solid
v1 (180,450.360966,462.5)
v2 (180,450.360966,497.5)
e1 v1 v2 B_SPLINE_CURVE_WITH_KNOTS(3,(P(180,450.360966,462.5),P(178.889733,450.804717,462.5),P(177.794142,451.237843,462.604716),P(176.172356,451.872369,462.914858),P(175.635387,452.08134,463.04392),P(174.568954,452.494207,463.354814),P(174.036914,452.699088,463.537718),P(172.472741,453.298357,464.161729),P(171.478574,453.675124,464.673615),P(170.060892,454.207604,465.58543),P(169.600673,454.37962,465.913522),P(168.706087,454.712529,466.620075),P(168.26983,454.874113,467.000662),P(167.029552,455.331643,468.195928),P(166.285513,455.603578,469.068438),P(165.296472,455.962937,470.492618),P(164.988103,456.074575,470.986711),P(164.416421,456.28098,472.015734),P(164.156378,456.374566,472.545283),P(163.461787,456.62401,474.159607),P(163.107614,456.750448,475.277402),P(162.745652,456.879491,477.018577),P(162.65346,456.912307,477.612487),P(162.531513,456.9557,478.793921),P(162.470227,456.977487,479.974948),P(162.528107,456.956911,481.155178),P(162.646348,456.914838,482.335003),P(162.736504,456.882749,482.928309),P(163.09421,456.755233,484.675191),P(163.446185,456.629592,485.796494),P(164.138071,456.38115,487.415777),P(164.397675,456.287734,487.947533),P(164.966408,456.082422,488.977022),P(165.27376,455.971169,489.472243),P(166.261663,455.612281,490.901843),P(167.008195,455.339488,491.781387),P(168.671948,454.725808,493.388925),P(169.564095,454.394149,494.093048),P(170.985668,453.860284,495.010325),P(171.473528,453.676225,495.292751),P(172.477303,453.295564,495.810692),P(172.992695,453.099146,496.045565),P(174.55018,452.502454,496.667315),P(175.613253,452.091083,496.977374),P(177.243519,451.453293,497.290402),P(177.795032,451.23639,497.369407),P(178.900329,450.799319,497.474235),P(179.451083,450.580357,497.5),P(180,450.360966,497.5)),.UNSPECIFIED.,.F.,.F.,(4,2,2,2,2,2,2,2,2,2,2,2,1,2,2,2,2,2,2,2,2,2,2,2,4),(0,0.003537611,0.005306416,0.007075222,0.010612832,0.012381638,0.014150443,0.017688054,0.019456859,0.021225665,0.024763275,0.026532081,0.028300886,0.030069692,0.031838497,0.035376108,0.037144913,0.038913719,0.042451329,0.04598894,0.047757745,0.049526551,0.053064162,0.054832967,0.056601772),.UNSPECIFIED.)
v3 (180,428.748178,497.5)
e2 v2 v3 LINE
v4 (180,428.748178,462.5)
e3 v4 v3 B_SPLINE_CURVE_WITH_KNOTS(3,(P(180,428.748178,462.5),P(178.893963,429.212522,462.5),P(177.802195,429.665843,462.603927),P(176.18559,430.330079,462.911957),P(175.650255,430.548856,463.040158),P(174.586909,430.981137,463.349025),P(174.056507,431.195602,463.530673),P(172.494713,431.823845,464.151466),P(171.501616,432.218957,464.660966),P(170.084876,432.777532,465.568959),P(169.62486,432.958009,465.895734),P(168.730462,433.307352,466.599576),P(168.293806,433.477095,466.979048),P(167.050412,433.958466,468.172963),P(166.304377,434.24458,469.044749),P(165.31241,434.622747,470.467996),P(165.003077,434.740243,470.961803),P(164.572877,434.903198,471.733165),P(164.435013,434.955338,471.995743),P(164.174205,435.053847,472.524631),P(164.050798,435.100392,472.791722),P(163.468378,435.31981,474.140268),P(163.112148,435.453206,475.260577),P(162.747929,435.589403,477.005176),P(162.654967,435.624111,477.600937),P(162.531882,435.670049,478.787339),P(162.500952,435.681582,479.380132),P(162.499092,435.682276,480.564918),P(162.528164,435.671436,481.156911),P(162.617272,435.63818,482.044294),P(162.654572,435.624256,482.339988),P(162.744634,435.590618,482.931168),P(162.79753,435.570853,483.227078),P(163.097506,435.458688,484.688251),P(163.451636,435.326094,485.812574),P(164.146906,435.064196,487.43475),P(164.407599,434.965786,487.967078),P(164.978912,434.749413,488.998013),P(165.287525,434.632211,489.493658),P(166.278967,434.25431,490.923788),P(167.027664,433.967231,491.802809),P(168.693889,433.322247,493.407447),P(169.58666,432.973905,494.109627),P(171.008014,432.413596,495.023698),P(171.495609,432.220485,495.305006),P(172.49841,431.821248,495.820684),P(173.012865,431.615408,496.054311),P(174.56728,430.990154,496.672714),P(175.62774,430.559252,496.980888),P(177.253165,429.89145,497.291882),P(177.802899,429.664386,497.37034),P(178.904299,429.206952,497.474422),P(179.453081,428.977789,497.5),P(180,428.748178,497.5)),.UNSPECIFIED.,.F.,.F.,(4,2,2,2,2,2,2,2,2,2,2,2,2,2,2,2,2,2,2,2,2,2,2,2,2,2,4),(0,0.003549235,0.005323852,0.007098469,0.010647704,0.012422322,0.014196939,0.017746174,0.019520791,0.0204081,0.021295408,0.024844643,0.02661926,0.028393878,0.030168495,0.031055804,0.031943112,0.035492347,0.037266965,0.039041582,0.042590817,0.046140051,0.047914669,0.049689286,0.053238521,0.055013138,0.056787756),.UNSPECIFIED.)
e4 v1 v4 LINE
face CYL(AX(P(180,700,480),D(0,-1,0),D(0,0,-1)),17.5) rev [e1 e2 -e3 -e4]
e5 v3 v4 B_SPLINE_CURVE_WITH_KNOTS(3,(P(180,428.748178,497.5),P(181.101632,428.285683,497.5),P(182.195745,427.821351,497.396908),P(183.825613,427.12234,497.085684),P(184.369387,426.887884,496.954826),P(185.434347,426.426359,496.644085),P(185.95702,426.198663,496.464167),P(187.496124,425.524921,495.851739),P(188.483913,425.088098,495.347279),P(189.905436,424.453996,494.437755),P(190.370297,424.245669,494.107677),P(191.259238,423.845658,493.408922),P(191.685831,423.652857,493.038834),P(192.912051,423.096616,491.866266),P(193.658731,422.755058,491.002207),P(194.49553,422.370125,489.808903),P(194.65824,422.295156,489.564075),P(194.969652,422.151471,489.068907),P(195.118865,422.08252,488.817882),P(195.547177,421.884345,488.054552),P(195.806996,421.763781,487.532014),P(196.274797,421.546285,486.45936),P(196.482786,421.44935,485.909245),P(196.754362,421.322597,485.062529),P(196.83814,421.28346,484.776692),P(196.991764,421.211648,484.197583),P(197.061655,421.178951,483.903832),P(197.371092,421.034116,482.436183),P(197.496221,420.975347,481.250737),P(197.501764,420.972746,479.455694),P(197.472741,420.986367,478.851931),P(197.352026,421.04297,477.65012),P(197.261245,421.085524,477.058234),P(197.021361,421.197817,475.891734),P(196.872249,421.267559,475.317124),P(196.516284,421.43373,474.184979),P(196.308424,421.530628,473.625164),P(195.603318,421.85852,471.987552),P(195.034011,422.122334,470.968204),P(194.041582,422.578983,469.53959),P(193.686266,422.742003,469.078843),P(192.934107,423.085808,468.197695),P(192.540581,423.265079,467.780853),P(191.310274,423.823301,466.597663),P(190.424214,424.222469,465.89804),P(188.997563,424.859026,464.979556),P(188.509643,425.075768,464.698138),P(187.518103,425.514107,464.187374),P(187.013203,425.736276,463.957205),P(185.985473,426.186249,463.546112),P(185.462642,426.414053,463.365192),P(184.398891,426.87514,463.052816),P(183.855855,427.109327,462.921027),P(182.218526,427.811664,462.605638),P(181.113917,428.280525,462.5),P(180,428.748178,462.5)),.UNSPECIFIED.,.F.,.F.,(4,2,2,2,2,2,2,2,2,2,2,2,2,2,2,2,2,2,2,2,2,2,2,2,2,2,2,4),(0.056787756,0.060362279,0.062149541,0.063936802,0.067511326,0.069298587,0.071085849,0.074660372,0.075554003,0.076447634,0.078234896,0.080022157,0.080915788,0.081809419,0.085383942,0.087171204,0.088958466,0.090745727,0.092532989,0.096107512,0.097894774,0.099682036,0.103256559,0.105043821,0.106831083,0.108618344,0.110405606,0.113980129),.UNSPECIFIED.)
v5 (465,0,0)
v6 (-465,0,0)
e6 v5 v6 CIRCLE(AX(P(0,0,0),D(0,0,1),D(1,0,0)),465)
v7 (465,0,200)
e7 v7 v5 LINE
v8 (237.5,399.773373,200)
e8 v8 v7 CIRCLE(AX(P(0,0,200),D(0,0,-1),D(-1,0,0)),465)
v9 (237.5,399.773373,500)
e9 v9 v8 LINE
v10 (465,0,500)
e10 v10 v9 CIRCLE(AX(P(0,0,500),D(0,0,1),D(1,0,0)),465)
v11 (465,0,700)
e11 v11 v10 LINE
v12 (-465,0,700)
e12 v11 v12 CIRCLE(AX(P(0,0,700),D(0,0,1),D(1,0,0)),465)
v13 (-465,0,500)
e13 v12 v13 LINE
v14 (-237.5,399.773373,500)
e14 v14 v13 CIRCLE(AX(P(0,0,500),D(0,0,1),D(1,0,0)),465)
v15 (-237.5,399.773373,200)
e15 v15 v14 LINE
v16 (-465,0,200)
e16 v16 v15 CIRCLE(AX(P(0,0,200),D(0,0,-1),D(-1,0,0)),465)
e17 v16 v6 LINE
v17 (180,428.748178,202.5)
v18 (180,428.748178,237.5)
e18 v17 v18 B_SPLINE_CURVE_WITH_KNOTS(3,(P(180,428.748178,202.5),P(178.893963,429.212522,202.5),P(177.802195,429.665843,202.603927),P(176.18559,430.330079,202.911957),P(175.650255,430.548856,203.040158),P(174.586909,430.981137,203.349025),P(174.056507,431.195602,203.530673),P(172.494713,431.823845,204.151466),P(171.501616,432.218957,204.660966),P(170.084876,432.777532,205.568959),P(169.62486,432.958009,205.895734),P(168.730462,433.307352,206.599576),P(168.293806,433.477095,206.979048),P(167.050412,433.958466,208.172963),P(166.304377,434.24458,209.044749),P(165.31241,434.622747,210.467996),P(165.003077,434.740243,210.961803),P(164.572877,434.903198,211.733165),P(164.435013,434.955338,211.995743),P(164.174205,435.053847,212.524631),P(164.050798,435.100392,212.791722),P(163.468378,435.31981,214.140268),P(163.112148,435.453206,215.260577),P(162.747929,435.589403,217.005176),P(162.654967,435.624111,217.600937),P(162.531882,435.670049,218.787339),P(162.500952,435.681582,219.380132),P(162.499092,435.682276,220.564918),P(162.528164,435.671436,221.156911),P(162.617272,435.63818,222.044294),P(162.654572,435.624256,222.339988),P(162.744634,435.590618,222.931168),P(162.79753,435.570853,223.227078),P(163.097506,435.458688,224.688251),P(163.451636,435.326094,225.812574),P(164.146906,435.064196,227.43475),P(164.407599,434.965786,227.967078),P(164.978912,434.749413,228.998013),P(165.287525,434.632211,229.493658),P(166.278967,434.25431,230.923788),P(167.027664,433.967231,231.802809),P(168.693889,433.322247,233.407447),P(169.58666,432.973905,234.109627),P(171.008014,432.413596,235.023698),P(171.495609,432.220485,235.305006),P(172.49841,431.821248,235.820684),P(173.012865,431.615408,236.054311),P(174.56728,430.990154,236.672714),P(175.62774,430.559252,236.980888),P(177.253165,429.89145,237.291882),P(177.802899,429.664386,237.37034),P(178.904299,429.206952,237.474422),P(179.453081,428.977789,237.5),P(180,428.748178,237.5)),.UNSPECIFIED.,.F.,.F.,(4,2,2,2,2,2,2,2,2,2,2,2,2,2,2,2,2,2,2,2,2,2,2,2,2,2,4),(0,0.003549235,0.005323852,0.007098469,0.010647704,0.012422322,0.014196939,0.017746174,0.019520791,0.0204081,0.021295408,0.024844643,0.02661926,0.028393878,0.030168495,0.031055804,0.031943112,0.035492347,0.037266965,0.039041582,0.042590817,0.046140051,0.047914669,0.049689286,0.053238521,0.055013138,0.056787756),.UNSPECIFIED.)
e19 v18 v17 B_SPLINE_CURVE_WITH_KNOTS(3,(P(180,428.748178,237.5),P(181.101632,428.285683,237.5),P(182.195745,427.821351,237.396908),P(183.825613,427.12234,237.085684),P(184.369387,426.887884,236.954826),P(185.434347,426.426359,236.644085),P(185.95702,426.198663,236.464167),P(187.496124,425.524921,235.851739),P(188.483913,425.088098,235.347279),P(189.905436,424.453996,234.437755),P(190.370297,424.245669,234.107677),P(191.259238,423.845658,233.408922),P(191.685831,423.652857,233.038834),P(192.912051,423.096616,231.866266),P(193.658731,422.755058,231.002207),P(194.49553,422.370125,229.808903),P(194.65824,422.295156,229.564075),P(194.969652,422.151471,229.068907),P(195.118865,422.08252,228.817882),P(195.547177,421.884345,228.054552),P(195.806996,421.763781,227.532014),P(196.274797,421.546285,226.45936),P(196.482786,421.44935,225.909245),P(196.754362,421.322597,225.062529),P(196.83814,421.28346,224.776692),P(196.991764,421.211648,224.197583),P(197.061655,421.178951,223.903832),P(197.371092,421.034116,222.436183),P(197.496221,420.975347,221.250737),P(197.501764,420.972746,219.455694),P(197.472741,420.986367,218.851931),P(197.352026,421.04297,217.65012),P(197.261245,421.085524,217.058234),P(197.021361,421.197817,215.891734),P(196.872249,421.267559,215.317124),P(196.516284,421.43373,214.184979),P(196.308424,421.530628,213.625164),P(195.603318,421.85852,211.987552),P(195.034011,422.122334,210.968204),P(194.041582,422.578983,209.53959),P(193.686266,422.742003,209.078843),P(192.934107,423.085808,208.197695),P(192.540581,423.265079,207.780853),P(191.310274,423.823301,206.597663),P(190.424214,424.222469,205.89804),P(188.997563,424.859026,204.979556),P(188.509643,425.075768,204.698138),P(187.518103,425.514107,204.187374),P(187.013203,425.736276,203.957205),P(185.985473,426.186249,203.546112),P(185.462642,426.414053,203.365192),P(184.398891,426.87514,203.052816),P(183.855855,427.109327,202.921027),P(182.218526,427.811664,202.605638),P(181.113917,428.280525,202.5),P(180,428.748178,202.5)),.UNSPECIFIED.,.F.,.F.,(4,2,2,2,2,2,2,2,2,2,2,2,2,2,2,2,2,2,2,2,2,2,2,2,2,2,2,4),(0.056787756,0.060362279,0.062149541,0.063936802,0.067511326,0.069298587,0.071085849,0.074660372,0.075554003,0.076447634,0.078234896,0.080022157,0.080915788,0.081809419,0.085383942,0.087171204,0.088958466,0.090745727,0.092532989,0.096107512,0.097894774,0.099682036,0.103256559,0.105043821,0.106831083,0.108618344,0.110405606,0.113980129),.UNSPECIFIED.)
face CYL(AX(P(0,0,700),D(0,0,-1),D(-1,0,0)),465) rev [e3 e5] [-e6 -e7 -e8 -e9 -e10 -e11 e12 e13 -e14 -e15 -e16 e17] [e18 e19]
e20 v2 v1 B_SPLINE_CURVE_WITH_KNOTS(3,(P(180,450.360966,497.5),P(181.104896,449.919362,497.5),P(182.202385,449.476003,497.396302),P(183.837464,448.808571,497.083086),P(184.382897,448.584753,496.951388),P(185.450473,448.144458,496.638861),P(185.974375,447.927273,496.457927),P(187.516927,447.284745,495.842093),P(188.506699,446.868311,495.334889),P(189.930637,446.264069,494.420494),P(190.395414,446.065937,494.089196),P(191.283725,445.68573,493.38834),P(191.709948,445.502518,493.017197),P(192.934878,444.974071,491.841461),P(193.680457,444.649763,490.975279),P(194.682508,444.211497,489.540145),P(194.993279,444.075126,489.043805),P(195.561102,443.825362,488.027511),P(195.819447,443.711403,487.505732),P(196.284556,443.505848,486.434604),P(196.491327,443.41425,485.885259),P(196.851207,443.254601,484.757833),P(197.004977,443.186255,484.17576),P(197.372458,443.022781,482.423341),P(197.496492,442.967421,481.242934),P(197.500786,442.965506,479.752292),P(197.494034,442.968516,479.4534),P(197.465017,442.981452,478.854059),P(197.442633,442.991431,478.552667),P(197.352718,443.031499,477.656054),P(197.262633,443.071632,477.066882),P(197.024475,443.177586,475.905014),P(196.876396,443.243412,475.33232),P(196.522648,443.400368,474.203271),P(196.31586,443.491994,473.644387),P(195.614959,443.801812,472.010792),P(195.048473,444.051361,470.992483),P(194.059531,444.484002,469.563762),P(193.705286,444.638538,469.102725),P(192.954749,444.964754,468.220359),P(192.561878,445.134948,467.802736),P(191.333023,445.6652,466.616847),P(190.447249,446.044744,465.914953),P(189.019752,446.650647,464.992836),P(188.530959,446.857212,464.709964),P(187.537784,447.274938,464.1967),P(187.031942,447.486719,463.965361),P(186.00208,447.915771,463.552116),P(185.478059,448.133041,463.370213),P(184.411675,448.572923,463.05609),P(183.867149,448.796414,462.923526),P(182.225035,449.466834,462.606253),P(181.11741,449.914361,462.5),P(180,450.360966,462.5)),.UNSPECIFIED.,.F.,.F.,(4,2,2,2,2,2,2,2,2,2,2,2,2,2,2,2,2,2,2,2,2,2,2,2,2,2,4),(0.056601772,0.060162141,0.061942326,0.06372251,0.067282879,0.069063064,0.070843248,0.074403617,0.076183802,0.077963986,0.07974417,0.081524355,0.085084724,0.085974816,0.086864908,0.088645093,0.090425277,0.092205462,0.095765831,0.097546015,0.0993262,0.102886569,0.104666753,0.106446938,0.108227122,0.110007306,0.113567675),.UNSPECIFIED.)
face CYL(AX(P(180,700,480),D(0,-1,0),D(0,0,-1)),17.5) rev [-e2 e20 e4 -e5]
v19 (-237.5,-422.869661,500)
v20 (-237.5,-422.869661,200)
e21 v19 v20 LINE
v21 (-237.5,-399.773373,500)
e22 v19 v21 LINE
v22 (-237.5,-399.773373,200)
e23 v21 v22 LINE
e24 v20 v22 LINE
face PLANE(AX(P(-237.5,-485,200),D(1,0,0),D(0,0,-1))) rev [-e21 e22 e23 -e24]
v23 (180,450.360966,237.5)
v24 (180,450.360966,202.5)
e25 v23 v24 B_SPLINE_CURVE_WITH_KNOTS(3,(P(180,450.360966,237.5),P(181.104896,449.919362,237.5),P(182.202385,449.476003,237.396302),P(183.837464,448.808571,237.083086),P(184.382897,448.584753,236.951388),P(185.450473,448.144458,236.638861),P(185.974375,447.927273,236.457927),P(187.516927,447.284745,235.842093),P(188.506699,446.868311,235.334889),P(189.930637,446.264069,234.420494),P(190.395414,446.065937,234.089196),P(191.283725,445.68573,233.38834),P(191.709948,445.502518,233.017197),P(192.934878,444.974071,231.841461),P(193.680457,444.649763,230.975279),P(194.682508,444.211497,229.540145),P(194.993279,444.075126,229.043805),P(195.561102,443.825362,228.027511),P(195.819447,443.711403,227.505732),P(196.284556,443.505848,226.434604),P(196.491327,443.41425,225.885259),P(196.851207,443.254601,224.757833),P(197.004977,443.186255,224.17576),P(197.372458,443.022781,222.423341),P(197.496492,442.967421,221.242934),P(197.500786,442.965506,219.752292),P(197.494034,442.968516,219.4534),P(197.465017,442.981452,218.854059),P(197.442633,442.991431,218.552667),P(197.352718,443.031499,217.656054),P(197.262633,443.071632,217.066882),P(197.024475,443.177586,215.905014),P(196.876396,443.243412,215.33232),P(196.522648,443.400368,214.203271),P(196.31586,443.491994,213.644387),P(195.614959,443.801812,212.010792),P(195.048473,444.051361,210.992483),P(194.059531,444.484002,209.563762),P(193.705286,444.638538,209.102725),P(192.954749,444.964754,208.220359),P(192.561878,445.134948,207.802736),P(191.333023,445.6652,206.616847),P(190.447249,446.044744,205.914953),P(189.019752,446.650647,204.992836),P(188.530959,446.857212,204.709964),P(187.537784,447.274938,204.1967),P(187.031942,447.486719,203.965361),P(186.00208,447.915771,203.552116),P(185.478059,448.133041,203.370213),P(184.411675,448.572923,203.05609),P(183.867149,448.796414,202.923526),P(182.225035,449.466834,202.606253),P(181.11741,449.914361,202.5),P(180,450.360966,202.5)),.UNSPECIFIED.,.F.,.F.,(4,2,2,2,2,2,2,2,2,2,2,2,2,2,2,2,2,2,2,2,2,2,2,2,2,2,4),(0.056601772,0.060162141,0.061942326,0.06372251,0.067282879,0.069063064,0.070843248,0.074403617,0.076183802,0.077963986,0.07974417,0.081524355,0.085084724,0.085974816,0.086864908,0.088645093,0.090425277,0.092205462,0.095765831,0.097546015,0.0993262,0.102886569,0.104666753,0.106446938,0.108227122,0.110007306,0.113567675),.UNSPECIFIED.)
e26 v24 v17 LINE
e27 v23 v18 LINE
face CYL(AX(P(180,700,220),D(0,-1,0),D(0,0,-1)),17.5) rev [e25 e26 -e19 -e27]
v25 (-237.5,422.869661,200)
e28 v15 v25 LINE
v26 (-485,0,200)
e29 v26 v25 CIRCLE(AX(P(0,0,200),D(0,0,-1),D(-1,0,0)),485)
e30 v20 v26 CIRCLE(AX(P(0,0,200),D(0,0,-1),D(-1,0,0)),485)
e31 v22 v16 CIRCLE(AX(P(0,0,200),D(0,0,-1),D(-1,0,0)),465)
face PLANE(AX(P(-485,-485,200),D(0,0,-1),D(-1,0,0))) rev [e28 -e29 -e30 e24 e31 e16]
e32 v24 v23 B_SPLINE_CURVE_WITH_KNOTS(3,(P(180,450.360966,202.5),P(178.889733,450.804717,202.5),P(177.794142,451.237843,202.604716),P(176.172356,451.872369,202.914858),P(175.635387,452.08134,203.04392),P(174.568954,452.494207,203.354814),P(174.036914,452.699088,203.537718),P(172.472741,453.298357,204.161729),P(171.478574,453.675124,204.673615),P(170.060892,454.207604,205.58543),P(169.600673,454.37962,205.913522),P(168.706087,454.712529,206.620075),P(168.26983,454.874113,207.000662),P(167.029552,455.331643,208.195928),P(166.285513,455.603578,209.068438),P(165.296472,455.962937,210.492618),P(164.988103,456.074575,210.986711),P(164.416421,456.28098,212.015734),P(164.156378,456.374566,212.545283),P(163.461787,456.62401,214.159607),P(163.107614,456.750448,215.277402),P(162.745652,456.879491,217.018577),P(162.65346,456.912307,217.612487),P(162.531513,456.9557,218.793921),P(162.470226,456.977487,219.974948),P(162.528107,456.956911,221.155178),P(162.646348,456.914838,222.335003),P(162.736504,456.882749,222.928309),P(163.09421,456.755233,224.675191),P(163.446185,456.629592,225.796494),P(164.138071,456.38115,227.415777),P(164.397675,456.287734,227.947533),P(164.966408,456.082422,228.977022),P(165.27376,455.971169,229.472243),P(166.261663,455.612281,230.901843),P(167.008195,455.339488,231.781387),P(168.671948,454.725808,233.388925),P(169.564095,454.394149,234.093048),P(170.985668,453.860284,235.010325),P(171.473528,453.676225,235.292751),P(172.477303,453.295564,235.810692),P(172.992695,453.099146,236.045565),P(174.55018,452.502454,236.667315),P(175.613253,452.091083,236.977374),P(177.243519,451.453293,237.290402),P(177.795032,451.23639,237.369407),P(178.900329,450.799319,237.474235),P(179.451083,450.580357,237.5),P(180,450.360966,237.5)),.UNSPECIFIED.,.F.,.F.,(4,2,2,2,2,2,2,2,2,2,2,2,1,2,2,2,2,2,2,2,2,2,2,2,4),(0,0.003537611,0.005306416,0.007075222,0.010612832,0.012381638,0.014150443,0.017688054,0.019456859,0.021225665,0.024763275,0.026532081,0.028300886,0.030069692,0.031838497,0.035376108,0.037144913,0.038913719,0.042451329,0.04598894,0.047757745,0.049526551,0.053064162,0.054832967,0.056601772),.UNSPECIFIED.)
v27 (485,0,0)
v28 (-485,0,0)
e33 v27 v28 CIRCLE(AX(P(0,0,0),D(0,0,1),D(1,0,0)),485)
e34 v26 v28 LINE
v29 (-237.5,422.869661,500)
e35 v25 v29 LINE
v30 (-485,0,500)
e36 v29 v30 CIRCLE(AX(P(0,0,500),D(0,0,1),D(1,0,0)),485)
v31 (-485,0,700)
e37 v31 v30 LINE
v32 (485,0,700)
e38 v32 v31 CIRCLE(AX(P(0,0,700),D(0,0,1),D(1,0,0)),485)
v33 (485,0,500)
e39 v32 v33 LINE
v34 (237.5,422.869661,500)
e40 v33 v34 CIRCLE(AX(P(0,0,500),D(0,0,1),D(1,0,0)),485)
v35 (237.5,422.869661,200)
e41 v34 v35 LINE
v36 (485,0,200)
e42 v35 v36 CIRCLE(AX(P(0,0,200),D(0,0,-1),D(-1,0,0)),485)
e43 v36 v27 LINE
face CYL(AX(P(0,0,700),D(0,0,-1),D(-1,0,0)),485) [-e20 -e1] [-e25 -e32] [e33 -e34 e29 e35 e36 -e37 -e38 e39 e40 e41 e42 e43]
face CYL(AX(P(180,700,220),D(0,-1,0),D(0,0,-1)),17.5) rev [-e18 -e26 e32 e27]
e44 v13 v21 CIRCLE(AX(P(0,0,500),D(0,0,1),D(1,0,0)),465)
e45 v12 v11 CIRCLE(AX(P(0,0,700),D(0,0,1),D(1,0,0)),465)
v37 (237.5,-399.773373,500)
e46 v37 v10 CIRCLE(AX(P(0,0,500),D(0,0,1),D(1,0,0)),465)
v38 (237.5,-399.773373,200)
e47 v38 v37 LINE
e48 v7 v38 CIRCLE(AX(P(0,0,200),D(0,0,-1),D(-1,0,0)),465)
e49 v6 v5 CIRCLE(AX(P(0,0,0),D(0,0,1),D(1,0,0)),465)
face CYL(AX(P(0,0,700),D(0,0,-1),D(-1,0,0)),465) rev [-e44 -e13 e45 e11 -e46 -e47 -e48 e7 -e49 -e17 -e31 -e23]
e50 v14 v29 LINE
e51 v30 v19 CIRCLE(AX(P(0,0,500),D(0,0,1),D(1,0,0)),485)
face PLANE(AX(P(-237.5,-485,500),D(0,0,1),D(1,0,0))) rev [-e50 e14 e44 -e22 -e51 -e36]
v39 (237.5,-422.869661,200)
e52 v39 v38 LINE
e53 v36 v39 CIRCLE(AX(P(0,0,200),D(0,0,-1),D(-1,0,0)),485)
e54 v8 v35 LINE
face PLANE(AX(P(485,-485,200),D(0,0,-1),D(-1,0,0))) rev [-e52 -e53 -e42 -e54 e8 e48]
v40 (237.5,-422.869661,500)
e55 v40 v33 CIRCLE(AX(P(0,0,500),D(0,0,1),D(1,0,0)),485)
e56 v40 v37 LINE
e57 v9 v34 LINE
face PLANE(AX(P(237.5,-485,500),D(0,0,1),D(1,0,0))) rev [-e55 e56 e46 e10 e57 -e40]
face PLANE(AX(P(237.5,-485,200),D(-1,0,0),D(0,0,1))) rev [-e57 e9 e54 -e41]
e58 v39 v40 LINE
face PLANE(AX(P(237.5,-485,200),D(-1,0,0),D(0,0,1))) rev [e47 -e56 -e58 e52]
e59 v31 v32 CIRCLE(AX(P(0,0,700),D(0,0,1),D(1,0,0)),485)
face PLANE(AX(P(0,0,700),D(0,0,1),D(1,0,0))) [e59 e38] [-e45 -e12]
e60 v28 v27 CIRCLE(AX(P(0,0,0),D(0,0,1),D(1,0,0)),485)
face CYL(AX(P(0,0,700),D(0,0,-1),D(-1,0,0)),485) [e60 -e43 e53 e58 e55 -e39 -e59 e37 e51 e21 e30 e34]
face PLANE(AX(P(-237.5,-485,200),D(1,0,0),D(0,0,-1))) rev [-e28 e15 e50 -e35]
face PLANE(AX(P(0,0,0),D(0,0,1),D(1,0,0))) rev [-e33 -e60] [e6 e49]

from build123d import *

# Parameters (mm, degrees)
SKETCH1_R               = 485
SKETCH1_R_2             = 465
BOSS_EXTRUDE1_DEPTH     = 700
CUT_EXTRUDE1_DEPTH      = 981.025509872
CUT_EXTRUDE1_DEPTH_BACK = 981.025509872
SKETCH2_W               = 247.5
SKETCH2_H               = 300
SKETCH3_R               = 17.5
CUT_EXTRUDE2_DEPTH      = 700


with BuildPart() as part:
    # Sketch1 → Boss-Extrude1 (new body)
    with BuildSketch(Plane.XY):
        Circle(SKETCH1_R)
        Circle(SKETCH1_R_2, mode=Mode.SUBTRACT)
    extrude(amount=BOSS_EXTRUDE1_DEPTH)

    # Sketch2 → Cut-Extrude1 (cut, two sides: drawn at the far end of the back side and taken through both)
    with BuildSketch(Plane(origin=(0, 0, 0), x_dir=(1, 0, 0), z_dir=(0, 1, 0)).offset(-CUT_EXTRUDE1_DEPTH_BACK)):
        with Locations((361.25, -350)):
            Rectangle(SKETCH2_W, SKETCH2_H)
        with Locations((-361.25, -350)):
            Rectangle(SKETCH2_W, SKETCH2_H)
    extrude(amount=CUT_EXTRUDE1_DEPTH + CUT_EXTRUDE1_DEPTH_BACK, mode=Mode.SUBTRACT)

    # Sketch3 → Cut-Extrude2 (cut)
    with BuildSketch(Plane(origin=(0, 0, 0), x_dir=(1, 0, 0), z_dir=(0, 1, 0))):
        with Locations(Location((180, -220, 0), (0, 0, 90))):
            Circle(SKETCH3_R)
        with Locations(Location((180, -480, 0), (0, 0, 90))):
            Circle(SKETCH3_R)
    extrude(amount=CUT_EXTRUDE2_DEPTH, mode=Mode.SUBTRACT)


solid = part.part
